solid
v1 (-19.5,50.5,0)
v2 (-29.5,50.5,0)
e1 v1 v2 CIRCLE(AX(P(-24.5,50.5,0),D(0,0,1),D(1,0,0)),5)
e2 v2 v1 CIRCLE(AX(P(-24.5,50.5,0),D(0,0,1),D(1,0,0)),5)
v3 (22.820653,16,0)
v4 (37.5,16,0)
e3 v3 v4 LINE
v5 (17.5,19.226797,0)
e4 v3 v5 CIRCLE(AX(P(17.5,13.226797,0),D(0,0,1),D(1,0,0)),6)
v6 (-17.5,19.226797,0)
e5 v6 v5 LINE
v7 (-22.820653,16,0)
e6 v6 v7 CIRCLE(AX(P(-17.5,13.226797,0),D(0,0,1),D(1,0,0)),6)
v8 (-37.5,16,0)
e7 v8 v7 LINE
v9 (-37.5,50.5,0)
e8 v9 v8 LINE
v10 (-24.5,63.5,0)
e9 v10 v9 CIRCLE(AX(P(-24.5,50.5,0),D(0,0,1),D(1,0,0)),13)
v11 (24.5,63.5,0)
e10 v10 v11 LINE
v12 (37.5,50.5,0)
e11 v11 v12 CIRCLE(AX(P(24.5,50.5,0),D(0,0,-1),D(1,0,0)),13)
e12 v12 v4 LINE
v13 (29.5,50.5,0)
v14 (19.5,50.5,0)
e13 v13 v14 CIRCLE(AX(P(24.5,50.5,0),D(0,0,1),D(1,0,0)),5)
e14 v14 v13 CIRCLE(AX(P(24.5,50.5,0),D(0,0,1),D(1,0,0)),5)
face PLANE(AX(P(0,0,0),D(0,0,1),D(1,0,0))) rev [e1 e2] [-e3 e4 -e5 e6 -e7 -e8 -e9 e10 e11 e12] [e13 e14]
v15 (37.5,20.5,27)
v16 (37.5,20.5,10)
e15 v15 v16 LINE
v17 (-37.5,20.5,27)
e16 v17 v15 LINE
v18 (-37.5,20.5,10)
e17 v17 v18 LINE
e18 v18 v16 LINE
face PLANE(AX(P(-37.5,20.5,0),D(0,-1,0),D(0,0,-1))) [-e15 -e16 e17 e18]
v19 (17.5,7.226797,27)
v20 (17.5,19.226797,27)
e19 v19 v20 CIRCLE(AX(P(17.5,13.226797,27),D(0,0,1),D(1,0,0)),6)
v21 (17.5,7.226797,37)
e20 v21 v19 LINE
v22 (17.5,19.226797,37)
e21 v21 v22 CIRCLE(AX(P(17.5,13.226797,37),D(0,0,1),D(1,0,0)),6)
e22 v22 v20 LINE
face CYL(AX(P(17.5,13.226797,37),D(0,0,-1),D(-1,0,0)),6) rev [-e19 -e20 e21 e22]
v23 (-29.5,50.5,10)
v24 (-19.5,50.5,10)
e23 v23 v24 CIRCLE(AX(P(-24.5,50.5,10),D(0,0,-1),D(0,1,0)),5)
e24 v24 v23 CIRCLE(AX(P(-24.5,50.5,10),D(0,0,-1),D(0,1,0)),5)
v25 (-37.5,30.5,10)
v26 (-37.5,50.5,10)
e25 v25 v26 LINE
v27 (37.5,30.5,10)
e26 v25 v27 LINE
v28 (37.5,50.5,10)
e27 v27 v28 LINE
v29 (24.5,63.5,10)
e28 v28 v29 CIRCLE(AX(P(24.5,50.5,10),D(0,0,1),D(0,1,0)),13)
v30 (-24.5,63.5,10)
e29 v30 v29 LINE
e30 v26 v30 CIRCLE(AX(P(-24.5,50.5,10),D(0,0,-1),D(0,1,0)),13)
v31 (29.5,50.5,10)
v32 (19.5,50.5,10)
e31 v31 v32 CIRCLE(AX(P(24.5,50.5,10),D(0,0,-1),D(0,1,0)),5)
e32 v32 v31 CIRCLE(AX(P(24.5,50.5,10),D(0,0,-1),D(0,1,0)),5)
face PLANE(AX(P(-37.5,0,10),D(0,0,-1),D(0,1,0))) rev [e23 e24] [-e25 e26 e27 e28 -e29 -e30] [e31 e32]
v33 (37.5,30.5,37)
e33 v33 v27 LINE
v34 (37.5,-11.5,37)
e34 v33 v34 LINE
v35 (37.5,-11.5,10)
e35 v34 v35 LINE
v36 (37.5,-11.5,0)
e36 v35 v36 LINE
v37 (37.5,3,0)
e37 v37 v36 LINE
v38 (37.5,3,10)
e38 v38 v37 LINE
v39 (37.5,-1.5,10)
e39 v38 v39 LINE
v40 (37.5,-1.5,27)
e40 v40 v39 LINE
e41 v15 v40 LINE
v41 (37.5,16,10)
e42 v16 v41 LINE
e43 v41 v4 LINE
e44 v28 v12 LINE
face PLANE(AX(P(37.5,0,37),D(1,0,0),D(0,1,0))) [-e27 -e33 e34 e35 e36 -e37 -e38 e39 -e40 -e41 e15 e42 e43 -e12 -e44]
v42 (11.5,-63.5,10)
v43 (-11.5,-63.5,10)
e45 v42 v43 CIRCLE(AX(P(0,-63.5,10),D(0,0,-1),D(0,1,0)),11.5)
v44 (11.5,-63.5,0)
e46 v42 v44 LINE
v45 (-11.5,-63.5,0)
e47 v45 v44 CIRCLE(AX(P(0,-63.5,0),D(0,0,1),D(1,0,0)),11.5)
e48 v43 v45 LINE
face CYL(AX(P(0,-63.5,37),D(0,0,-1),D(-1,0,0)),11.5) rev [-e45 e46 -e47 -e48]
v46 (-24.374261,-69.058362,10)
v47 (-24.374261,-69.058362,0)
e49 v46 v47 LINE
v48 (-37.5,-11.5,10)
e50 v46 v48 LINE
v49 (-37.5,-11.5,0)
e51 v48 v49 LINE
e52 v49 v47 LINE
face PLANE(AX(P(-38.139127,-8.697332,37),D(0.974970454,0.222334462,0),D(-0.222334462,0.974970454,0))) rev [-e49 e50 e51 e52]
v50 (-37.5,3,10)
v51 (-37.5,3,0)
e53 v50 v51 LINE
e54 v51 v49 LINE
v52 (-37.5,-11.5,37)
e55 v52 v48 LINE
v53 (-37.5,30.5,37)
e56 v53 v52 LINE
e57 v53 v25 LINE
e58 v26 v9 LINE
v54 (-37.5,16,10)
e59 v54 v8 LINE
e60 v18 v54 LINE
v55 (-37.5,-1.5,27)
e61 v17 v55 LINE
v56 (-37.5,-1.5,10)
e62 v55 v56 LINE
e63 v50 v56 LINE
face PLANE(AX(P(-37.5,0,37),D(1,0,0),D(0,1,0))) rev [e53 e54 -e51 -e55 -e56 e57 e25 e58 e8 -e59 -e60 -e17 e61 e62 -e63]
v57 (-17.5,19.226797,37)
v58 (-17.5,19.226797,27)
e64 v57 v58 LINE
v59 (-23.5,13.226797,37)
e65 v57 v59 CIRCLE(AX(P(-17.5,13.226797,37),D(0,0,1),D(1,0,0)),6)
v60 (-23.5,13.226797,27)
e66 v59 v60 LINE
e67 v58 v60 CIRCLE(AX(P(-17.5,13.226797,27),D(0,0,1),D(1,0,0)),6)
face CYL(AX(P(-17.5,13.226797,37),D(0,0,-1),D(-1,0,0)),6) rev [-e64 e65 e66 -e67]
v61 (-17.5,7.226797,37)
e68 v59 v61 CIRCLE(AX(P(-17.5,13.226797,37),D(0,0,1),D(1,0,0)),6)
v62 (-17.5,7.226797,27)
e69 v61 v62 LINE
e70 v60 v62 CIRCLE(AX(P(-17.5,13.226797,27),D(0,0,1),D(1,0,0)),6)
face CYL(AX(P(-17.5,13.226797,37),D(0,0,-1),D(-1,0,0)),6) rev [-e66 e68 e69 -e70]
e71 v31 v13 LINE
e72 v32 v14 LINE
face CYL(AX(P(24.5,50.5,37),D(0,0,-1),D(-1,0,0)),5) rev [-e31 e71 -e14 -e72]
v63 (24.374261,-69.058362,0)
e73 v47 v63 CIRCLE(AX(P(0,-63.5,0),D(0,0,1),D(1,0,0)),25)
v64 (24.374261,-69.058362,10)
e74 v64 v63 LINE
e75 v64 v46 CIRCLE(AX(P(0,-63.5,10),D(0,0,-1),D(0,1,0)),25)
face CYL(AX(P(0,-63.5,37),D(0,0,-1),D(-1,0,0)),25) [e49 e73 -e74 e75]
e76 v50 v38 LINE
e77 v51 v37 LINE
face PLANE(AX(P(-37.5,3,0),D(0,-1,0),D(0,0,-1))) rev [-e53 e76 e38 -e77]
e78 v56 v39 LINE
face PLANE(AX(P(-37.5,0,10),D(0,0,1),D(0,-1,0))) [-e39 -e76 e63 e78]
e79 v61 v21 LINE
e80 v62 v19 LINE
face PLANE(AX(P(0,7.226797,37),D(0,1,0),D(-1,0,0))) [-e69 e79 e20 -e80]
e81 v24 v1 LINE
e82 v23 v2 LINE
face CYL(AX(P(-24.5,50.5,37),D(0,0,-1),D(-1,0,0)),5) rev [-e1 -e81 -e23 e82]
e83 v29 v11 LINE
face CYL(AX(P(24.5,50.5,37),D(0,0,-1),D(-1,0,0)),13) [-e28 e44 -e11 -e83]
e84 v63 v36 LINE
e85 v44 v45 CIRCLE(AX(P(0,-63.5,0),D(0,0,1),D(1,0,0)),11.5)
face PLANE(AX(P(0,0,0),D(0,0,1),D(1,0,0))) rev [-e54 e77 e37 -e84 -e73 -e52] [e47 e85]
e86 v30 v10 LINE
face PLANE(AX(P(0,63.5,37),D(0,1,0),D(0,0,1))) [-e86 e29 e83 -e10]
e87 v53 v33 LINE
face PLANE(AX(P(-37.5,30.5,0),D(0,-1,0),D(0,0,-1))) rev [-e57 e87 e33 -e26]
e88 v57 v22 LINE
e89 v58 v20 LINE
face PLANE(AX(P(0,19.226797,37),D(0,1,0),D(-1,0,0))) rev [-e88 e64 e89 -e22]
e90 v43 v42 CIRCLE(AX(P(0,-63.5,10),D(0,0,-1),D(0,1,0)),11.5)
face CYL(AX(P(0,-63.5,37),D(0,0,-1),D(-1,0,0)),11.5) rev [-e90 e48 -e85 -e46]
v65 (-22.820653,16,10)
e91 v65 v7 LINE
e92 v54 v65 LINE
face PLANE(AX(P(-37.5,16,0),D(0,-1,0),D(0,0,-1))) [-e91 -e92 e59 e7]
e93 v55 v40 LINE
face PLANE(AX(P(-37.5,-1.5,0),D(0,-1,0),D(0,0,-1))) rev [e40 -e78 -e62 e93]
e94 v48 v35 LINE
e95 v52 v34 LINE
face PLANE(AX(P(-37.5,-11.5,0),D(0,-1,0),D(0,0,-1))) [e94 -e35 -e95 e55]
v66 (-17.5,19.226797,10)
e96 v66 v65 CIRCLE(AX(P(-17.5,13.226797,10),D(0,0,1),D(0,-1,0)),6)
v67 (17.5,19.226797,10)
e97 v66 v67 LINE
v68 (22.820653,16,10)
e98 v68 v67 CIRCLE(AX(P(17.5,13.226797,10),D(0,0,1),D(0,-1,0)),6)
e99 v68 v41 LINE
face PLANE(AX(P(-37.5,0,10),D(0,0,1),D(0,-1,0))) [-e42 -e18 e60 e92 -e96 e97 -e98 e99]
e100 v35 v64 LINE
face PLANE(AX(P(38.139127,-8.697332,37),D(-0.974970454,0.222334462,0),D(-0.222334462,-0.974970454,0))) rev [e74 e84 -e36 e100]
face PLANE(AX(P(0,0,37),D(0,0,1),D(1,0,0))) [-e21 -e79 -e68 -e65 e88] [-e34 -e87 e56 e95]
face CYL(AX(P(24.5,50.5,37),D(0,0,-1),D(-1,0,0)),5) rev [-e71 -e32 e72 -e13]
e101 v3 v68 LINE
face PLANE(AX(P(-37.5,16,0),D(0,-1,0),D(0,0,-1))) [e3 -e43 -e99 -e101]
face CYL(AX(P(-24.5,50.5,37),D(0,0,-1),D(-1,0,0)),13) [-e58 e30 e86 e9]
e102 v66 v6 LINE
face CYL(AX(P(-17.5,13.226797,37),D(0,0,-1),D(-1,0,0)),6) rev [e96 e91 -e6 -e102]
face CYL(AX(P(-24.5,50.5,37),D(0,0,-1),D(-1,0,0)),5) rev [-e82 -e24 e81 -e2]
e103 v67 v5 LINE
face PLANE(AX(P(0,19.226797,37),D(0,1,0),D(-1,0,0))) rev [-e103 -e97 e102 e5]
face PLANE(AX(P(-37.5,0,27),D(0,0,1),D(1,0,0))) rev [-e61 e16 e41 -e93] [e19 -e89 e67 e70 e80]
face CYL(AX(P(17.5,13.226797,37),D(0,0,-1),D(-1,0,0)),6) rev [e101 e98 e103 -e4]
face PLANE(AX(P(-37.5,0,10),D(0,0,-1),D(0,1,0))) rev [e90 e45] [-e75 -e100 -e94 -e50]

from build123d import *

# Parameters (mm, degrees)
BRACKET_PROFILE_SKETCH_R        = 5
BRACKET_PROFILE_SKETCH_R_2      = 11.5
BRACKET_BODY_DEPTH              = 37
SLOT_AND_CHANNEL_CUT_DEPTH      = 103.992718189
SLOT_AND_CHANNEL_CUT_DEPTH_BACK = 103.992718189
SLOT_AND_CHANNEL_SKETCH_W       = 27
SLOT_AND_CHANNEL_SKETCH_H       = 33
SLOT_AND_CHANNEL_SKETCH_H_2     = 77


with BuildPart() as part:
    # Bracket Profile Sketch → Bracket Body (new body)
    with BuildSketch(Plane.XY):
        with BuildLine():
            Line((-24.5, 63.5), (24.5, 63.5))
            ThreePointArc((24.5, 63.5), (33.692388155, 59.692388155), (37.5, 50.5))
            Line((37.5, 50.5), (37.5, -11.5))
            Line((37.5, -11.5), (24.374261359, -69.058361557))
            ThreePointArc((24.374261359, -69.058361557), (0, -88.5), (-24.374261359, -69.058361557))
            Line((-24.374261359, -69.058361557), (-37.5, -11.5))
            Line((-37.5, -11.5), (-37.5, 50.5))
            ThreePointArc((-37.5, 50.5), (-33.692388155, 59.692388155), (-24.5, 63.5))
        make_face()
        with Locations((24.5, 50.5)):
            Circle(BRACKET_PROFILE_SKETCH_R, mode=Mode.SUBTRACT)
        with Locations((-24.5, 50.5)):
            Circle(BRACKET_PROFILE_SKETCH_R, mode=Mode.SUBTRACT)
        with Locations((0, -63.5)):
            Circle(BRACKET_PROFILE_SKETCH_R_2, mode=Mode.SUBTRACT)
        with BuildLine():
            ThreePointArc((17.5, 7.226797096), (23.5, 13.226797096), (17.5, 19.226797096))
            Line((17.5, 19.226797096), (-17.5, 19.226797096))
            ThreePointArc((-17.5, 19.226797096), (-23.5, 13.226797096), (-17.5, 7.226797096))
            Line((-17.5, 7.226797096), (17.5, 7.226797096))
        make_face(mode=Mode.SUBTRACT)
    extrude(amount=BRACKET_BODY_DEPTH)

    # Slot and Channel Sketch → Slot and Channel Cut (cut, two sides: drawn at the far end of the back side and taken through both)
    with BuildSketch(Plane(origin=(0, 0, 0), x_dir=(0, 0, -1), z_dir=(1, 0, 0)).offset(-SLOT_AND_CHANNEL_CUT_DEPTH_BACK)):
        with Locations((-23.5, 47)):
            Rectangle(SLOT_AND_CHANNEL_SKETCH_W, SLOT_AND_CHANNEL_SKETCH_H)
        Polygon((0, 3), (0, 16), (-10, 16), (-10, 20.5), (-27, 20.5), (-27, -1.5), (-10, -1.5), (-10, 3), align=None)
        with Locations((-23.5, -50)):
            Rectangle(SLOT_AND_CHANNEL_SKETCH_W, SLOT_AND_CHANNEL_SKETCH_H_2)
    extrude(amount=SLOT_AND_CHANNEL_CUT_DEPTH + SLOT_AND_CHANNEL_CUT_DEPTH_BACK, mode=Mode.SUBTRACT)


solid = part.part
